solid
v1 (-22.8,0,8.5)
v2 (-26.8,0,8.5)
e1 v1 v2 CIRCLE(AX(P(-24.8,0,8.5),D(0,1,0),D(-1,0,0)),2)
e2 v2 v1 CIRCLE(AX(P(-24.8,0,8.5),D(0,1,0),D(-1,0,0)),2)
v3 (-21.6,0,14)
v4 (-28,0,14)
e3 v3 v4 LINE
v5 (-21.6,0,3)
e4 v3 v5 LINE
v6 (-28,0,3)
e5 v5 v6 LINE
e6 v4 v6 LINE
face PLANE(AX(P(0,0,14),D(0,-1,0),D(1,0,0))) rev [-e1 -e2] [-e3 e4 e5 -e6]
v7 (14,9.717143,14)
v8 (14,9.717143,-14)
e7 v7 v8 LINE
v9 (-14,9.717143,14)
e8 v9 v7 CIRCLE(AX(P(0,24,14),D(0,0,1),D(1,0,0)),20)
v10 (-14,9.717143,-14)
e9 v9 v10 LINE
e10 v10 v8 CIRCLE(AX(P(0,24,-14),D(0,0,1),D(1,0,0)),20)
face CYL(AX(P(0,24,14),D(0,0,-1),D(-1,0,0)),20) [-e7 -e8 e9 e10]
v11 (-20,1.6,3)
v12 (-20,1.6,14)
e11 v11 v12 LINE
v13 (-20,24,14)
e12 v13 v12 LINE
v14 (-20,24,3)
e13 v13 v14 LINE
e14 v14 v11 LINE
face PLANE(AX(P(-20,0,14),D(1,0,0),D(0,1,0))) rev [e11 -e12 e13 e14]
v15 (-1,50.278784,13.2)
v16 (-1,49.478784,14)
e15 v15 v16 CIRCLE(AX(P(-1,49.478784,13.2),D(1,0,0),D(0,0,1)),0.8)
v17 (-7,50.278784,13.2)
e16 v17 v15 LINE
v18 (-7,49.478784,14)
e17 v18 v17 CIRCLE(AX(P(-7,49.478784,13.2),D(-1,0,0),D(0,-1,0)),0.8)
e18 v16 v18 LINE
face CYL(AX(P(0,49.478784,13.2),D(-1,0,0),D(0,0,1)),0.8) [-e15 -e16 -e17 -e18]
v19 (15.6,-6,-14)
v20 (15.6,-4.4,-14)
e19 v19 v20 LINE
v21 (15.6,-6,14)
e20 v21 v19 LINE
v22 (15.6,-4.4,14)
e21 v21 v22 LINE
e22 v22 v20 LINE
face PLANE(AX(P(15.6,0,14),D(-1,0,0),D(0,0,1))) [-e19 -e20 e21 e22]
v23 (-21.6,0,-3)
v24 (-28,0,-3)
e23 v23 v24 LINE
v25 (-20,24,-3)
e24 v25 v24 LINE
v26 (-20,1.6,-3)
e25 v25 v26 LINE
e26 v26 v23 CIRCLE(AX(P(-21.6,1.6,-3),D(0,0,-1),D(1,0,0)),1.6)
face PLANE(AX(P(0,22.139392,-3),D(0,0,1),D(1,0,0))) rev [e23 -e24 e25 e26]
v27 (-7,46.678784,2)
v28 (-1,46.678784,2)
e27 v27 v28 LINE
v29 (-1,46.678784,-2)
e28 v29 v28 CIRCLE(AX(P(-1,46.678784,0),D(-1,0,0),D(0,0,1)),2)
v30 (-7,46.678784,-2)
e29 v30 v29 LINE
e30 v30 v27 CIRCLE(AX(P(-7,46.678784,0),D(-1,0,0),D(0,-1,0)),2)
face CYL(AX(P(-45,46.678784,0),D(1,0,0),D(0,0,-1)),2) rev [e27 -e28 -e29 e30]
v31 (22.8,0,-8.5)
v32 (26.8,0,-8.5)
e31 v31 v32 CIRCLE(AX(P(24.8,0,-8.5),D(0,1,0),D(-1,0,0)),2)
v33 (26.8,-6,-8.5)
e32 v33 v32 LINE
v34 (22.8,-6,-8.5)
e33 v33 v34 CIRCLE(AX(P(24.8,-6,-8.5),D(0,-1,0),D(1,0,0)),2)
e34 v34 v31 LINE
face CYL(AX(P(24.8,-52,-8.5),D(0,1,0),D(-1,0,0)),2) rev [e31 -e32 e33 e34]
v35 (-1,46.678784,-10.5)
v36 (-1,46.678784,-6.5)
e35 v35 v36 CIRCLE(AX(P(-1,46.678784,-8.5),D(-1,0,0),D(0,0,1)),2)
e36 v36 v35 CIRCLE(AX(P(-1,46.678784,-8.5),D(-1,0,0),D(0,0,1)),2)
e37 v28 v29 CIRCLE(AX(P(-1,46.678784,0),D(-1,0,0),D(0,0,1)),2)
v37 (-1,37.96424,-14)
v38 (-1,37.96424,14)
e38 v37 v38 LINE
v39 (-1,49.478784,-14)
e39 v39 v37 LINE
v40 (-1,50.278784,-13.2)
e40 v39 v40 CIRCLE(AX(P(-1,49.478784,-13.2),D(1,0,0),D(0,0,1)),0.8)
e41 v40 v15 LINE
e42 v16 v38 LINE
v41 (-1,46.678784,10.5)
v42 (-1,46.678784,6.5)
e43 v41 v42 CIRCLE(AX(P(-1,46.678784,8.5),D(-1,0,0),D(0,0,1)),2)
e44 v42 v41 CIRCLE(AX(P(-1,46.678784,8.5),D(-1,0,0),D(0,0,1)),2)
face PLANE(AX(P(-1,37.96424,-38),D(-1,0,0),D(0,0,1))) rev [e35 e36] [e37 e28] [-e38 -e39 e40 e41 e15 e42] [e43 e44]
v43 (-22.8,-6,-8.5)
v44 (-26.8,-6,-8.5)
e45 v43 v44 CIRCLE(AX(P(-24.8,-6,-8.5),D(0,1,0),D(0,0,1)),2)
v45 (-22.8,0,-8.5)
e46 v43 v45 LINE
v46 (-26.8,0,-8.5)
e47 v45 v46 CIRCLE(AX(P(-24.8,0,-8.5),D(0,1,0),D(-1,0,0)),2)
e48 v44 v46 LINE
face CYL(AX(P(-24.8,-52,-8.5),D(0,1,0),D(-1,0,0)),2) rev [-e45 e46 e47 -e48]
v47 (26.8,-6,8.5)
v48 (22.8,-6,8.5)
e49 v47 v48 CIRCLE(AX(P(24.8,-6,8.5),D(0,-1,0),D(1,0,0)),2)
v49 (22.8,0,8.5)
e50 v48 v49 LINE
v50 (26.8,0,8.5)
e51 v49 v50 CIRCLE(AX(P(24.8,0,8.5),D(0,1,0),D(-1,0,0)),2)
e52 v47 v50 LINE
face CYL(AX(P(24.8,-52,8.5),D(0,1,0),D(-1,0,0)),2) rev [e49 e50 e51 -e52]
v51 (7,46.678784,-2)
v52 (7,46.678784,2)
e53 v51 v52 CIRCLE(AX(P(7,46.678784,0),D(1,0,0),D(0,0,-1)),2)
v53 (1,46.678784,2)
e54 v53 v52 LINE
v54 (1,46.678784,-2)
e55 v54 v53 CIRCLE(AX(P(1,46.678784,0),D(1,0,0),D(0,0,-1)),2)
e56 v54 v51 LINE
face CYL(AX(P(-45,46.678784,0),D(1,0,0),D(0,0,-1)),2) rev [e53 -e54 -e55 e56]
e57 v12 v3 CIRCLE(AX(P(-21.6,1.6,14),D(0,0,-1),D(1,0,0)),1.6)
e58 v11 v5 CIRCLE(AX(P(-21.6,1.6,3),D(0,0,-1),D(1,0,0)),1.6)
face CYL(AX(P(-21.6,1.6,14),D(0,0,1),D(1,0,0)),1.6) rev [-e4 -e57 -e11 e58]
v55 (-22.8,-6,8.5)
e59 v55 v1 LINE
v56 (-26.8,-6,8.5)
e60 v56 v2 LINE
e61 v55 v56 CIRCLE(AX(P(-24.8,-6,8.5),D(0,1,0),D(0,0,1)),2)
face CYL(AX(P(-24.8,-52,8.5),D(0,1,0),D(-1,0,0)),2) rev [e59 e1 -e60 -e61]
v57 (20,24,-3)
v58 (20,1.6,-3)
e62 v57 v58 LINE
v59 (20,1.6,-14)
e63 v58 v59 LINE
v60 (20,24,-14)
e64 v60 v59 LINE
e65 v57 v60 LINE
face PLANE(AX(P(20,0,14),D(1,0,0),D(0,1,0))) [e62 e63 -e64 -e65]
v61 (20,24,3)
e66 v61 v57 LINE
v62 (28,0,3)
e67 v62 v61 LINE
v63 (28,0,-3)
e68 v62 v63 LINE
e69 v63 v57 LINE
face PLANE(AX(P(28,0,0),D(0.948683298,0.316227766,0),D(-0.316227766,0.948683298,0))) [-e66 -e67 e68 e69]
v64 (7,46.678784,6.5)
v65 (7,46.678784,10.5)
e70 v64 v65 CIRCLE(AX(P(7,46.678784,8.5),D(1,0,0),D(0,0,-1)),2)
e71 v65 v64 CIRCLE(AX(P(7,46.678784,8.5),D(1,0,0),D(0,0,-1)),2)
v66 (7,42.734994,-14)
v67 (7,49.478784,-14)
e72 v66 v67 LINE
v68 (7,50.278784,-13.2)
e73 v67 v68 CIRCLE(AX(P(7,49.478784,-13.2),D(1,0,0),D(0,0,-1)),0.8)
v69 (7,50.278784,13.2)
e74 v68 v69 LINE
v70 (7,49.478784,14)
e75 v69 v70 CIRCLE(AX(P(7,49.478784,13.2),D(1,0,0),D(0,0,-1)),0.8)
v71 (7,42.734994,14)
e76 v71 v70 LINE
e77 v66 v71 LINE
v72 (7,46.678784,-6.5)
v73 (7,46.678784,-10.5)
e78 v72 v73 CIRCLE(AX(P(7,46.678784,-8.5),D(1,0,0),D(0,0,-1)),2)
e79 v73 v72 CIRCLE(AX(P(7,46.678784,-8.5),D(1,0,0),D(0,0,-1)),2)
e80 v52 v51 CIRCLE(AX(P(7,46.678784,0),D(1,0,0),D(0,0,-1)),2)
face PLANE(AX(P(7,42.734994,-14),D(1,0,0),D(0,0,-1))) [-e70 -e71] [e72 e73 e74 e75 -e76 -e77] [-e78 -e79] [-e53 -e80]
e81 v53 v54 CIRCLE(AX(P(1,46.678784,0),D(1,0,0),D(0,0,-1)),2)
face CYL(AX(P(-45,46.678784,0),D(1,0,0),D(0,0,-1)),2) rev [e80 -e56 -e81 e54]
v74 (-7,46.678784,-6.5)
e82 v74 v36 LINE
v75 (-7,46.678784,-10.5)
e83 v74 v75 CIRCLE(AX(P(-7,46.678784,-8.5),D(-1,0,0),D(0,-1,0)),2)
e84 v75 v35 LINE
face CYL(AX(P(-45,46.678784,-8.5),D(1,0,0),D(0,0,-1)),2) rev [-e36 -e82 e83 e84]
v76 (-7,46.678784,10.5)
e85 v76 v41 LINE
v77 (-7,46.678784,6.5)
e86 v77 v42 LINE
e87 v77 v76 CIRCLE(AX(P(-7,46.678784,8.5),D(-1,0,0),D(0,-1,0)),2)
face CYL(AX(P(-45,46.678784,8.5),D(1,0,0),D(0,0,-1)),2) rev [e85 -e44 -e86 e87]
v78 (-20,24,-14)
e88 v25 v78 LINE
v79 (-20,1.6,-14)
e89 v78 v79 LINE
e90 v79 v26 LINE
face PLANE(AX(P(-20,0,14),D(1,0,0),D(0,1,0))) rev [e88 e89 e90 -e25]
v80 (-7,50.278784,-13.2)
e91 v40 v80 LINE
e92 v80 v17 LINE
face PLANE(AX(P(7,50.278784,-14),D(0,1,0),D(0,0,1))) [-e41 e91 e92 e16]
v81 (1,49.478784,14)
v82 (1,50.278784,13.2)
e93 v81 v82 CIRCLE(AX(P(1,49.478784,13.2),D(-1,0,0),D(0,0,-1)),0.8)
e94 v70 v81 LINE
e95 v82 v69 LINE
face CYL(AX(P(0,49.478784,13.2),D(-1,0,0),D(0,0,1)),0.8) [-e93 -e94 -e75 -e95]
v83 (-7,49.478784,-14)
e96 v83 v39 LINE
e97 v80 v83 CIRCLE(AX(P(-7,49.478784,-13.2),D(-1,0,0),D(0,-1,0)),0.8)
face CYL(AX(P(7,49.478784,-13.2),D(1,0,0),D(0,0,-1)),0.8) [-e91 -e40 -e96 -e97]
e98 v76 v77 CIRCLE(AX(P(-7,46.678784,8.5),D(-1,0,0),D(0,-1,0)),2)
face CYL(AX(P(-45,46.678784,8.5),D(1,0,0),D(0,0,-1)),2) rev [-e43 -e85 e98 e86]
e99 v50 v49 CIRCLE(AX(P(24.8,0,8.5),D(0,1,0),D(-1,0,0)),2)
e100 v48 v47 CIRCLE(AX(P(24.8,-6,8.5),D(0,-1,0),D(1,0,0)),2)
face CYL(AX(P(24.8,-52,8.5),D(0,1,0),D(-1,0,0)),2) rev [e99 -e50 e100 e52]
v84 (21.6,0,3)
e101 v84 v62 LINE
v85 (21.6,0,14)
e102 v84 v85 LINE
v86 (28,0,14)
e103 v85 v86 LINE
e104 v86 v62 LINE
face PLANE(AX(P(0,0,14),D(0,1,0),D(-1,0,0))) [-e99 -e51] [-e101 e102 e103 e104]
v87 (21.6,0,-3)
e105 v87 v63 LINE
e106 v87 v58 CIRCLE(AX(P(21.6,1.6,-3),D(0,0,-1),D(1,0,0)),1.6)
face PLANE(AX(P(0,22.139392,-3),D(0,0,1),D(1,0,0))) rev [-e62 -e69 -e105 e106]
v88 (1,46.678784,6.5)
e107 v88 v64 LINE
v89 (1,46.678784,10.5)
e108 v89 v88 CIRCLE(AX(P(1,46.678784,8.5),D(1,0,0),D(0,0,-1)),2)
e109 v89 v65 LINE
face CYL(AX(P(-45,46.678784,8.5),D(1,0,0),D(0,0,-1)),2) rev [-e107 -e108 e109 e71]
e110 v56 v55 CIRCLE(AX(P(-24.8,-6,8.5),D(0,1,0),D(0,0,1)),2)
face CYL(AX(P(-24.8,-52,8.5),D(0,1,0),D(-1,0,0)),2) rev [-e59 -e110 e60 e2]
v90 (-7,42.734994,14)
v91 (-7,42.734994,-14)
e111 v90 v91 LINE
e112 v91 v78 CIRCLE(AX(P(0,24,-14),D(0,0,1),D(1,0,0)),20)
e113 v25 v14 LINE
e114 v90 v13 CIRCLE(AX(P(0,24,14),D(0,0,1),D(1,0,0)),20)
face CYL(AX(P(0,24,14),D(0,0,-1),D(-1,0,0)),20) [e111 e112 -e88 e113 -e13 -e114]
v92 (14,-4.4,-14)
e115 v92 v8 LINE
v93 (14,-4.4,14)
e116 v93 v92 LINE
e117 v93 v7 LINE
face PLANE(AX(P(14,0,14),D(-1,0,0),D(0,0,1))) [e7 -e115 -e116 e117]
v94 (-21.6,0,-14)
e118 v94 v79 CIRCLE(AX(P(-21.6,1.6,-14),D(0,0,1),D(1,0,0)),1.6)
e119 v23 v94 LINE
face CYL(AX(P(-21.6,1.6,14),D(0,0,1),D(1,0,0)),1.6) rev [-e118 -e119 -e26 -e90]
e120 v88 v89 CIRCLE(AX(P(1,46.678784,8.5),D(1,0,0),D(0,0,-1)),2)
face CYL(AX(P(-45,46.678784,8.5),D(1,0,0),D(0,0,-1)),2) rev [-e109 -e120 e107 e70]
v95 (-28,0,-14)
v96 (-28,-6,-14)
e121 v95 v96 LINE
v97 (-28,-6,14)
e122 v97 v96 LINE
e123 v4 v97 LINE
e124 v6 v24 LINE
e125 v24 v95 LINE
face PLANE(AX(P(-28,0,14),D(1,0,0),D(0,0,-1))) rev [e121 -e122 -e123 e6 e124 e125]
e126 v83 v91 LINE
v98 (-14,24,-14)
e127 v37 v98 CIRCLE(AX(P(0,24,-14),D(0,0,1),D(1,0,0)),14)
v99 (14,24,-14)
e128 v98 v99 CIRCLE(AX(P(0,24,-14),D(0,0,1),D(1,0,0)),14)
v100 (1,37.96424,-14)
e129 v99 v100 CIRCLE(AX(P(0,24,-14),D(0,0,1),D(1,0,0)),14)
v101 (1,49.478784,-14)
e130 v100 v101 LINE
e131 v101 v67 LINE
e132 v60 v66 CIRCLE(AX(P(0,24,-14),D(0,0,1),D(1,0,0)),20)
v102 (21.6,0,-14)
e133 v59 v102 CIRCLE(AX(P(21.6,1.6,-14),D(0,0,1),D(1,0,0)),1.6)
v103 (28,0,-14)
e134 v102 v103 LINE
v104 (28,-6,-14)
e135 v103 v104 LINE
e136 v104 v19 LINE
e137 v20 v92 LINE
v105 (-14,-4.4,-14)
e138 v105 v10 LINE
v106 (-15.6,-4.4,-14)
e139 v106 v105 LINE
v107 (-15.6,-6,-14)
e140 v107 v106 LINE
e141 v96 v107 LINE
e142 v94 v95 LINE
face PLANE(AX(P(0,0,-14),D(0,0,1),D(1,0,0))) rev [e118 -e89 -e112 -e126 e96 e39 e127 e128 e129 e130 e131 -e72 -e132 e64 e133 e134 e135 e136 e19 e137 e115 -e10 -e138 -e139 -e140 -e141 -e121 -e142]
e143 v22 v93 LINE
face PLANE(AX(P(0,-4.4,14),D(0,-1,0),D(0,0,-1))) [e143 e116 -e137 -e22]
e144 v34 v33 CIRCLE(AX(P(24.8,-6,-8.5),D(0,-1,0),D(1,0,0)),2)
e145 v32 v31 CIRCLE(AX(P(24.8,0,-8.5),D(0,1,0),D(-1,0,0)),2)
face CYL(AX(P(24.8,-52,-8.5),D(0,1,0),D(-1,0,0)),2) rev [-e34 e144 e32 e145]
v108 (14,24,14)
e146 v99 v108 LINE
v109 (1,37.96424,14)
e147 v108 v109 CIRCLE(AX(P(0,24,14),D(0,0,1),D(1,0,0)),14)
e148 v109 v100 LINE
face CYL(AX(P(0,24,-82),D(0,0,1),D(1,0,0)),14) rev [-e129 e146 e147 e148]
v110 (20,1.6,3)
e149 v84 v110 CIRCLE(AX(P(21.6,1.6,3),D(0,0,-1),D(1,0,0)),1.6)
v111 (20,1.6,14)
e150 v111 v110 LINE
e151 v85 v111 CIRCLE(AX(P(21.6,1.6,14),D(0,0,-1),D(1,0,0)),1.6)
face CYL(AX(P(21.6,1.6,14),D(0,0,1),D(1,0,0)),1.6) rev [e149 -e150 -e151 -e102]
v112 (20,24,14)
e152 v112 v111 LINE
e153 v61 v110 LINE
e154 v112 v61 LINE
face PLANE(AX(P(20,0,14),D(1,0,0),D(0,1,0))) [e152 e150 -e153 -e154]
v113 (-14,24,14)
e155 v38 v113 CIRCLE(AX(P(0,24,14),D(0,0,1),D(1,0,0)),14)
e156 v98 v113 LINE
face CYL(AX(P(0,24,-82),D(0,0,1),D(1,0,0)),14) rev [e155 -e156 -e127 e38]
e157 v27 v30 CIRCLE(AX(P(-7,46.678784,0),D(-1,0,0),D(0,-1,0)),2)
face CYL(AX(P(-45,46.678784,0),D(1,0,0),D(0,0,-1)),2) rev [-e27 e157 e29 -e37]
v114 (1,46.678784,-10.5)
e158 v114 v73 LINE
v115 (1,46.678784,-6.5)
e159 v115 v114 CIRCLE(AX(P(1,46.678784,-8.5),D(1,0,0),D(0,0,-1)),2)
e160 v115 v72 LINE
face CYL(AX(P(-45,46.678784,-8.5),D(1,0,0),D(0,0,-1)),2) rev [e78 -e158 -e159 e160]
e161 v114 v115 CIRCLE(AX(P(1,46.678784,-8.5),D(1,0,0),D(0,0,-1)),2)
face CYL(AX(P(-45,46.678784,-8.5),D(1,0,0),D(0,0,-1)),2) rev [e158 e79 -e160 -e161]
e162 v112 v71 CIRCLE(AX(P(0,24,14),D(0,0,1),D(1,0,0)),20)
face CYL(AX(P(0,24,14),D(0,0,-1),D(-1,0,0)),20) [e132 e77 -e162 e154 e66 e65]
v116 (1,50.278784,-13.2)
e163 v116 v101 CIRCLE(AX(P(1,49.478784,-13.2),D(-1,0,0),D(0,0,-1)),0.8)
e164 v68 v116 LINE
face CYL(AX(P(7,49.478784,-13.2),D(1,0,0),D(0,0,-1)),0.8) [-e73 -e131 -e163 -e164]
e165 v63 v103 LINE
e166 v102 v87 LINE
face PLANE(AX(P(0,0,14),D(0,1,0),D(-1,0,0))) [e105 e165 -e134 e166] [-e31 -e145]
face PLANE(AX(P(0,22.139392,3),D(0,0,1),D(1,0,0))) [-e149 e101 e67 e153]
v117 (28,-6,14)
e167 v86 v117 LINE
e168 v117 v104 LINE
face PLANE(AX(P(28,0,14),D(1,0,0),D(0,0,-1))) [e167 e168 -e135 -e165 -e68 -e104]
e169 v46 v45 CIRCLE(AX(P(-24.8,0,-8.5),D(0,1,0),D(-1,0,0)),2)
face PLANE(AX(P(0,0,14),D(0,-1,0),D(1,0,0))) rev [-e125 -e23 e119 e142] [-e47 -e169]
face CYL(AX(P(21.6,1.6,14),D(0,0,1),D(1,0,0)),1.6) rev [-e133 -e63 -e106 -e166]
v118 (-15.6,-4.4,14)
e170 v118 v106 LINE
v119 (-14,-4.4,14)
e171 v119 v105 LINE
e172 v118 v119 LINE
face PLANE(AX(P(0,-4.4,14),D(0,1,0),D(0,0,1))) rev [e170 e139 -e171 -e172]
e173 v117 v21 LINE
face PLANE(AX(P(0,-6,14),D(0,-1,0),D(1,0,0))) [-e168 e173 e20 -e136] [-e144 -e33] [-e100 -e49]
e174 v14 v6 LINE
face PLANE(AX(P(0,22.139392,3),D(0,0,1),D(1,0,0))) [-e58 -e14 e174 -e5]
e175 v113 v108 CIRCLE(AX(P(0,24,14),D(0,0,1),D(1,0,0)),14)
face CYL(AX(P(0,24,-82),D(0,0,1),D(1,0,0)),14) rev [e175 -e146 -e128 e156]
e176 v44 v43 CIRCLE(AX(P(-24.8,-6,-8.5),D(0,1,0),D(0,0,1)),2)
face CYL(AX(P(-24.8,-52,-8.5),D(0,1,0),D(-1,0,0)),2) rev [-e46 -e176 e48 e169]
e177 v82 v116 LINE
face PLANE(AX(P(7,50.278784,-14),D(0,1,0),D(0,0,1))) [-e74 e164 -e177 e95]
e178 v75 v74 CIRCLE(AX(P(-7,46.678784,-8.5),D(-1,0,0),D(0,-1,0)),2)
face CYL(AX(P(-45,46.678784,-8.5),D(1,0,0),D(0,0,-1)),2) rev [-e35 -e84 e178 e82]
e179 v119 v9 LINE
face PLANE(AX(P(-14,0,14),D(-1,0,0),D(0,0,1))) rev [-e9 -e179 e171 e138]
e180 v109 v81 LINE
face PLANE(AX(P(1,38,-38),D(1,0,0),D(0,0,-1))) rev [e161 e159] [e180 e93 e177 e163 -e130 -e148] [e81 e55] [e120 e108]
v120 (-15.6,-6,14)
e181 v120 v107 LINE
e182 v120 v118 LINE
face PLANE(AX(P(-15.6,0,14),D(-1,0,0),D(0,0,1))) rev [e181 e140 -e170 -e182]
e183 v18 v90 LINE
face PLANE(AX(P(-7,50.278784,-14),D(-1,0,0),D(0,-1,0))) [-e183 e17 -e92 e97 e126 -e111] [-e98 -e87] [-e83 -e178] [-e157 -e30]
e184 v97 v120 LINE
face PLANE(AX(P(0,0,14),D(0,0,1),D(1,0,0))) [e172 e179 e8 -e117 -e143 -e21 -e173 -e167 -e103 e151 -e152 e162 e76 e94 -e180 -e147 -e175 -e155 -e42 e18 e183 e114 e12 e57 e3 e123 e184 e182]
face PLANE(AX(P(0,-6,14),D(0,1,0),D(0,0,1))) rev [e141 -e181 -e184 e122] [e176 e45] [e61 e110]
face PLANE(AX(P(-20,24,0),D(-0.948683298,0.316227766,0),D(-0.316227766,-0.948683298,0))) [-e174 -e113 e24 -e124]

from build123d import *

# Parameters (mm, degrees)
CLAMP_BODY_DEPTH             = 14
CLAMP_BORE_SKETCH_R          = 14
CLAMP_BORE_DEPTH             = 96
CLAMP_LUGS_DEPTH             = 28
SPLIT_SLOT_2MM_DEPTH         = 52
BODY_FILLET_R1_6_A_R         = 1.6
BODY_FILLET_R1_6_B_R         = 1.6
CLAMP_SCREW_HOLES_SKETCH_R   = 2
CLAMP_SCREW_HOLES_3X_DEPTH   = 52
SUPPORT_RIB_1_REACH          = 61.228
SUPPORT_RIB_1_SKETCH_WALL_W  = 145.754223634
SUPPORT_RIB_1_SKETCH_WALL_H  = 6
SUPPORT_RIB_2_REACH          = 61.228
SUPPORT_RIB_2_SKETCH_WALL_W  = 145.754223634
SUPPORT_RIB_2_SKETCH_WALL_H  = 6
BASE_MOUNTING_HOLES_SKETCH_R = 2
BASE_MOUNTING_HOLES_4X_DEPTH = 52
LUG_FILLET_R0_8_A_R          = 0.8
LUG_FILLET_R0_8_B_R          = 0.8
LUG_FILLET_R0_8_C_R          = 0.8
LUG_FILLET_R0_8_D_R          = 0.8


with BuildPart() as part:
    # Clamp Body Profile → Clamp Body (new, symmetric)
    with BuildSketch(Plane.XY):
        with BuildLine():
            Line((20, 24), (20, 0))
            Line((20, 0), (28, 0))
            Line((28, 0), (28, -6))
            Line((28, -6), (15.6, -6))
            Line((15.6, -6), (15.6, -4.4))
            Line((15.6, -4.4), (14, -4.4))
            Line((14, -4.4), (14, 9.717143143))
            ThreePointArc((14, 9.717143143), (0, 4), (-14, 9.717143143))
            Line((-14, 9.717143143), (-14, -4.4))
            Line((-14, -4.4), (-15.6, -4.4))
            Line((-15.6, -4.4), (-15.6, -6))
            Line((-15.6, -6), (-28, -6))
            Line((-28, -6), (-28, 0))
            Line((-28, 0), (-20, 0))
            Line((-20, 0), (-20, 24))
            ThreePointArc((-20, 24), (0, 44), (20, 24))
        make_face()
    extrude(amount=CLAMP_BODY_DEPTH, both=True)

    # Clamp Bore Sketch → Clamp Bore (cut)
    with BuildSketch(Plane.XY.offset(14)):
        with Locations((0, 24)):
            Circle(CLAMP_BORE_SKETCH_R)
    extrude(amount=-CLAMP_BORE_DEPTH, mode=Mode.SUBTRACT)

    # Clamp Lugs Sketch → Clamp Lugs (add)
    with BuildSketch(Plane.XY.offset(14)):
        Polygon((0, 38), (7, 38), (7, 42.734993995), (7, 50.278784028), (-7, 50.278784028), (-7, 38), align=None)
    extrude(amount=-CLAMP_LUGS_DEPTH)

    # Split Slot Sketch → Split Slot 2mm (cut)
    with BuildSketch(Plane.XY.offset(14)):
        Polygon((-1, 37.964240044), (-1, 37.406271495), (1, 37.406271495), (1, 38), (1, 50.278784028), (-1, 50.278784028), align=None)
    extrude(amount=-SPLIT_SLOT_2MM_DEPTH, mode=Mode.SUBTRACT)

    # Body Fillet R1.6 A
    body_fillet_r1_6_a_edges = [part.edges().sort_by_distance(p)[0] for p in [
        (20, 0, 0),
    ]]
    fillet(body_fillet_r1_6_a_edges, radius=BODY_FILLET_R1_6_A_R)

    # Body Fillet R1.6 B
    body_fillet_r1_6_b_edges = [part.edges().sort_by_distance(p)[0] for p in [
        (-20, 0, 0),
    ]]
    fillet(body_fillet_r1_6_b_edges, radius=BODY_FILLET_R1_6_B_R)

    # Clamp Screw Holes Sketch → Clamp Screw Holes 3x (cut)
    with BuildSketch(Plane(origin=(7, 0, 0), x_dir=(0, 0, -1), z_dir=(1, 0, 0))):
        with Locations((8.5, 46.678784028)):
            Circle(CLAMP_SCREW_HOLES_SKETCH_R)
        with Locations((-8.5, 46.678784028)):
            Circle(CLAMP_SCREW_HOLES_SKETCH_R)
        with Locations((0, 46.678784028)):
            Circle(CLAMP_SCREW_HOLES_SKETCH_R)
    extrude(amount=-CLAMP_SCREW_HOLES_3X_DEPTH, mode=Mode.SUBTRACT)

    # Support Rib 1 Sketch wall → Support Rib 1 (add, up to next)
    with BuildSketch(Plane(origin=(24, 12, 0), x_dir=(-0.316227766017, 0.948683298051, 0), z_dir=(-0.948683298051, -0.316227766017, 0)), mode=Mode.PRIVATE) as support_rib_1_sk1:
        Rectangle(SUPPORT_RIB_1_SKETCH_WALL_W, SUPPORT_RIB_1_SKETCH_WALL_H)
    support_rib_1_tool1 = extrude(support_rib_1_sk1.sketch, amount=SUPPORT_RIB_1_REACH, mode=Mode.PRIVATE) - part.part
    add(support_rib_1_tool1.solids().sort_by_distance((24, 12, 0))[0])

    # Support Rib 2 Sketch wall → Support Rib 2 (add, up to next)
    with BuildSketch(Plane(origin=(-24, 12, 0), x_dir=(-0.316227766017, -0.948683298051, 0), z_dir=(0.948683298051, -0.316227766017, 0)), mode=Mode.PRIVATE) as support_rib_2_sk1:
        Rectangle(SUPPORT_RIB_2_SKETCH_WALL_W, SUPPORT_RIB_2_SKETCH_WALL_H)
    support_rib_2_tool1 = extrude(support_rib_2_sk1.sketch, amount=SUPPORT_RIB_2_REACH, mode=Mode.PRIVATE) - part.part
    add(support_rib_2_tool1.solids().sort_by_distance((-24, 12, 0))[0])

    # Base Mounting Holes Sketch → Base Mounting Holes 4x (cut)
    with BuildSketch(Plane(origin=(0, 0, 0), x_dir=(1, 0, 0), z_dir=(0, 1, 0))):
        with Locations(Location((24.8, 8.5, 0), (0, 0, 180))):
            Circle(BASE_MOUNTING_HOLES_SKETCH_R)
        with Locations(Location((24.8, -8.5, 0), (0, 0, 180))):
            Circle(BASE_MOUNTING_HOLES_SKETCH_R)
        with Locations(Location((-24.8, 8.5, 0), (0, 0, 180))):
            Circle(BASE_MOUNTING_HOLES_SKETCH_R)
        with Locations(Location((-24.8, -8.5, 0), (0, 0, 180))):
            Circle(BASE_MOUNTING_HOLES_SKETCH_R)
    extrude(amount=-BASE_MOUNTING_HOLES_4X_DEPTH, mode=Mode.SUBTRACT)

    # Lug Fillet R0.8 A
    lug_fillet_r0_8_a_edges = [part.edges().sort_by_distance(p)[0] for p in [
        (4, 50.278784028, 14),
    ]]
    fillet(lug_fillet_r0_8_a_edges, radius=LUG_FILLET_R0_8_A_R)

    # Lug Fillet R0.8 B
    lug_fillet_r0_8_b_edges = [part.edges().sort_by_distance(p)[0] for p in [
        (-4, 50.278784028, 14),
    ]]
    fillet(lug_fillet_r0_8_b_edges, radius=LUG_FILLET_R0_8_B_R)

    # Lug Fillet R0.8 C
    lug_fillet_r0_8_c_edges = [part.edges().sort_by_distance(p)[0] for p in [
        (-4, 50.278784028, -14),
    ]]
    fillet(lug_fillet_r0_8_c_edges, radius=LUG_FILLET_R0_8_C_R)

    # Lug Fillet R0.8 D
    lug_fillet_r0_8_d_edges = [part.edges().sort_by_distance(p)[0] for p in [
        (4, 50.278784028, -14),
    ]]
    fillet(lug_fillet_r0_8_d_edges, radius=LUG_FILLET_R0_8_D_R)


solid = part.part
